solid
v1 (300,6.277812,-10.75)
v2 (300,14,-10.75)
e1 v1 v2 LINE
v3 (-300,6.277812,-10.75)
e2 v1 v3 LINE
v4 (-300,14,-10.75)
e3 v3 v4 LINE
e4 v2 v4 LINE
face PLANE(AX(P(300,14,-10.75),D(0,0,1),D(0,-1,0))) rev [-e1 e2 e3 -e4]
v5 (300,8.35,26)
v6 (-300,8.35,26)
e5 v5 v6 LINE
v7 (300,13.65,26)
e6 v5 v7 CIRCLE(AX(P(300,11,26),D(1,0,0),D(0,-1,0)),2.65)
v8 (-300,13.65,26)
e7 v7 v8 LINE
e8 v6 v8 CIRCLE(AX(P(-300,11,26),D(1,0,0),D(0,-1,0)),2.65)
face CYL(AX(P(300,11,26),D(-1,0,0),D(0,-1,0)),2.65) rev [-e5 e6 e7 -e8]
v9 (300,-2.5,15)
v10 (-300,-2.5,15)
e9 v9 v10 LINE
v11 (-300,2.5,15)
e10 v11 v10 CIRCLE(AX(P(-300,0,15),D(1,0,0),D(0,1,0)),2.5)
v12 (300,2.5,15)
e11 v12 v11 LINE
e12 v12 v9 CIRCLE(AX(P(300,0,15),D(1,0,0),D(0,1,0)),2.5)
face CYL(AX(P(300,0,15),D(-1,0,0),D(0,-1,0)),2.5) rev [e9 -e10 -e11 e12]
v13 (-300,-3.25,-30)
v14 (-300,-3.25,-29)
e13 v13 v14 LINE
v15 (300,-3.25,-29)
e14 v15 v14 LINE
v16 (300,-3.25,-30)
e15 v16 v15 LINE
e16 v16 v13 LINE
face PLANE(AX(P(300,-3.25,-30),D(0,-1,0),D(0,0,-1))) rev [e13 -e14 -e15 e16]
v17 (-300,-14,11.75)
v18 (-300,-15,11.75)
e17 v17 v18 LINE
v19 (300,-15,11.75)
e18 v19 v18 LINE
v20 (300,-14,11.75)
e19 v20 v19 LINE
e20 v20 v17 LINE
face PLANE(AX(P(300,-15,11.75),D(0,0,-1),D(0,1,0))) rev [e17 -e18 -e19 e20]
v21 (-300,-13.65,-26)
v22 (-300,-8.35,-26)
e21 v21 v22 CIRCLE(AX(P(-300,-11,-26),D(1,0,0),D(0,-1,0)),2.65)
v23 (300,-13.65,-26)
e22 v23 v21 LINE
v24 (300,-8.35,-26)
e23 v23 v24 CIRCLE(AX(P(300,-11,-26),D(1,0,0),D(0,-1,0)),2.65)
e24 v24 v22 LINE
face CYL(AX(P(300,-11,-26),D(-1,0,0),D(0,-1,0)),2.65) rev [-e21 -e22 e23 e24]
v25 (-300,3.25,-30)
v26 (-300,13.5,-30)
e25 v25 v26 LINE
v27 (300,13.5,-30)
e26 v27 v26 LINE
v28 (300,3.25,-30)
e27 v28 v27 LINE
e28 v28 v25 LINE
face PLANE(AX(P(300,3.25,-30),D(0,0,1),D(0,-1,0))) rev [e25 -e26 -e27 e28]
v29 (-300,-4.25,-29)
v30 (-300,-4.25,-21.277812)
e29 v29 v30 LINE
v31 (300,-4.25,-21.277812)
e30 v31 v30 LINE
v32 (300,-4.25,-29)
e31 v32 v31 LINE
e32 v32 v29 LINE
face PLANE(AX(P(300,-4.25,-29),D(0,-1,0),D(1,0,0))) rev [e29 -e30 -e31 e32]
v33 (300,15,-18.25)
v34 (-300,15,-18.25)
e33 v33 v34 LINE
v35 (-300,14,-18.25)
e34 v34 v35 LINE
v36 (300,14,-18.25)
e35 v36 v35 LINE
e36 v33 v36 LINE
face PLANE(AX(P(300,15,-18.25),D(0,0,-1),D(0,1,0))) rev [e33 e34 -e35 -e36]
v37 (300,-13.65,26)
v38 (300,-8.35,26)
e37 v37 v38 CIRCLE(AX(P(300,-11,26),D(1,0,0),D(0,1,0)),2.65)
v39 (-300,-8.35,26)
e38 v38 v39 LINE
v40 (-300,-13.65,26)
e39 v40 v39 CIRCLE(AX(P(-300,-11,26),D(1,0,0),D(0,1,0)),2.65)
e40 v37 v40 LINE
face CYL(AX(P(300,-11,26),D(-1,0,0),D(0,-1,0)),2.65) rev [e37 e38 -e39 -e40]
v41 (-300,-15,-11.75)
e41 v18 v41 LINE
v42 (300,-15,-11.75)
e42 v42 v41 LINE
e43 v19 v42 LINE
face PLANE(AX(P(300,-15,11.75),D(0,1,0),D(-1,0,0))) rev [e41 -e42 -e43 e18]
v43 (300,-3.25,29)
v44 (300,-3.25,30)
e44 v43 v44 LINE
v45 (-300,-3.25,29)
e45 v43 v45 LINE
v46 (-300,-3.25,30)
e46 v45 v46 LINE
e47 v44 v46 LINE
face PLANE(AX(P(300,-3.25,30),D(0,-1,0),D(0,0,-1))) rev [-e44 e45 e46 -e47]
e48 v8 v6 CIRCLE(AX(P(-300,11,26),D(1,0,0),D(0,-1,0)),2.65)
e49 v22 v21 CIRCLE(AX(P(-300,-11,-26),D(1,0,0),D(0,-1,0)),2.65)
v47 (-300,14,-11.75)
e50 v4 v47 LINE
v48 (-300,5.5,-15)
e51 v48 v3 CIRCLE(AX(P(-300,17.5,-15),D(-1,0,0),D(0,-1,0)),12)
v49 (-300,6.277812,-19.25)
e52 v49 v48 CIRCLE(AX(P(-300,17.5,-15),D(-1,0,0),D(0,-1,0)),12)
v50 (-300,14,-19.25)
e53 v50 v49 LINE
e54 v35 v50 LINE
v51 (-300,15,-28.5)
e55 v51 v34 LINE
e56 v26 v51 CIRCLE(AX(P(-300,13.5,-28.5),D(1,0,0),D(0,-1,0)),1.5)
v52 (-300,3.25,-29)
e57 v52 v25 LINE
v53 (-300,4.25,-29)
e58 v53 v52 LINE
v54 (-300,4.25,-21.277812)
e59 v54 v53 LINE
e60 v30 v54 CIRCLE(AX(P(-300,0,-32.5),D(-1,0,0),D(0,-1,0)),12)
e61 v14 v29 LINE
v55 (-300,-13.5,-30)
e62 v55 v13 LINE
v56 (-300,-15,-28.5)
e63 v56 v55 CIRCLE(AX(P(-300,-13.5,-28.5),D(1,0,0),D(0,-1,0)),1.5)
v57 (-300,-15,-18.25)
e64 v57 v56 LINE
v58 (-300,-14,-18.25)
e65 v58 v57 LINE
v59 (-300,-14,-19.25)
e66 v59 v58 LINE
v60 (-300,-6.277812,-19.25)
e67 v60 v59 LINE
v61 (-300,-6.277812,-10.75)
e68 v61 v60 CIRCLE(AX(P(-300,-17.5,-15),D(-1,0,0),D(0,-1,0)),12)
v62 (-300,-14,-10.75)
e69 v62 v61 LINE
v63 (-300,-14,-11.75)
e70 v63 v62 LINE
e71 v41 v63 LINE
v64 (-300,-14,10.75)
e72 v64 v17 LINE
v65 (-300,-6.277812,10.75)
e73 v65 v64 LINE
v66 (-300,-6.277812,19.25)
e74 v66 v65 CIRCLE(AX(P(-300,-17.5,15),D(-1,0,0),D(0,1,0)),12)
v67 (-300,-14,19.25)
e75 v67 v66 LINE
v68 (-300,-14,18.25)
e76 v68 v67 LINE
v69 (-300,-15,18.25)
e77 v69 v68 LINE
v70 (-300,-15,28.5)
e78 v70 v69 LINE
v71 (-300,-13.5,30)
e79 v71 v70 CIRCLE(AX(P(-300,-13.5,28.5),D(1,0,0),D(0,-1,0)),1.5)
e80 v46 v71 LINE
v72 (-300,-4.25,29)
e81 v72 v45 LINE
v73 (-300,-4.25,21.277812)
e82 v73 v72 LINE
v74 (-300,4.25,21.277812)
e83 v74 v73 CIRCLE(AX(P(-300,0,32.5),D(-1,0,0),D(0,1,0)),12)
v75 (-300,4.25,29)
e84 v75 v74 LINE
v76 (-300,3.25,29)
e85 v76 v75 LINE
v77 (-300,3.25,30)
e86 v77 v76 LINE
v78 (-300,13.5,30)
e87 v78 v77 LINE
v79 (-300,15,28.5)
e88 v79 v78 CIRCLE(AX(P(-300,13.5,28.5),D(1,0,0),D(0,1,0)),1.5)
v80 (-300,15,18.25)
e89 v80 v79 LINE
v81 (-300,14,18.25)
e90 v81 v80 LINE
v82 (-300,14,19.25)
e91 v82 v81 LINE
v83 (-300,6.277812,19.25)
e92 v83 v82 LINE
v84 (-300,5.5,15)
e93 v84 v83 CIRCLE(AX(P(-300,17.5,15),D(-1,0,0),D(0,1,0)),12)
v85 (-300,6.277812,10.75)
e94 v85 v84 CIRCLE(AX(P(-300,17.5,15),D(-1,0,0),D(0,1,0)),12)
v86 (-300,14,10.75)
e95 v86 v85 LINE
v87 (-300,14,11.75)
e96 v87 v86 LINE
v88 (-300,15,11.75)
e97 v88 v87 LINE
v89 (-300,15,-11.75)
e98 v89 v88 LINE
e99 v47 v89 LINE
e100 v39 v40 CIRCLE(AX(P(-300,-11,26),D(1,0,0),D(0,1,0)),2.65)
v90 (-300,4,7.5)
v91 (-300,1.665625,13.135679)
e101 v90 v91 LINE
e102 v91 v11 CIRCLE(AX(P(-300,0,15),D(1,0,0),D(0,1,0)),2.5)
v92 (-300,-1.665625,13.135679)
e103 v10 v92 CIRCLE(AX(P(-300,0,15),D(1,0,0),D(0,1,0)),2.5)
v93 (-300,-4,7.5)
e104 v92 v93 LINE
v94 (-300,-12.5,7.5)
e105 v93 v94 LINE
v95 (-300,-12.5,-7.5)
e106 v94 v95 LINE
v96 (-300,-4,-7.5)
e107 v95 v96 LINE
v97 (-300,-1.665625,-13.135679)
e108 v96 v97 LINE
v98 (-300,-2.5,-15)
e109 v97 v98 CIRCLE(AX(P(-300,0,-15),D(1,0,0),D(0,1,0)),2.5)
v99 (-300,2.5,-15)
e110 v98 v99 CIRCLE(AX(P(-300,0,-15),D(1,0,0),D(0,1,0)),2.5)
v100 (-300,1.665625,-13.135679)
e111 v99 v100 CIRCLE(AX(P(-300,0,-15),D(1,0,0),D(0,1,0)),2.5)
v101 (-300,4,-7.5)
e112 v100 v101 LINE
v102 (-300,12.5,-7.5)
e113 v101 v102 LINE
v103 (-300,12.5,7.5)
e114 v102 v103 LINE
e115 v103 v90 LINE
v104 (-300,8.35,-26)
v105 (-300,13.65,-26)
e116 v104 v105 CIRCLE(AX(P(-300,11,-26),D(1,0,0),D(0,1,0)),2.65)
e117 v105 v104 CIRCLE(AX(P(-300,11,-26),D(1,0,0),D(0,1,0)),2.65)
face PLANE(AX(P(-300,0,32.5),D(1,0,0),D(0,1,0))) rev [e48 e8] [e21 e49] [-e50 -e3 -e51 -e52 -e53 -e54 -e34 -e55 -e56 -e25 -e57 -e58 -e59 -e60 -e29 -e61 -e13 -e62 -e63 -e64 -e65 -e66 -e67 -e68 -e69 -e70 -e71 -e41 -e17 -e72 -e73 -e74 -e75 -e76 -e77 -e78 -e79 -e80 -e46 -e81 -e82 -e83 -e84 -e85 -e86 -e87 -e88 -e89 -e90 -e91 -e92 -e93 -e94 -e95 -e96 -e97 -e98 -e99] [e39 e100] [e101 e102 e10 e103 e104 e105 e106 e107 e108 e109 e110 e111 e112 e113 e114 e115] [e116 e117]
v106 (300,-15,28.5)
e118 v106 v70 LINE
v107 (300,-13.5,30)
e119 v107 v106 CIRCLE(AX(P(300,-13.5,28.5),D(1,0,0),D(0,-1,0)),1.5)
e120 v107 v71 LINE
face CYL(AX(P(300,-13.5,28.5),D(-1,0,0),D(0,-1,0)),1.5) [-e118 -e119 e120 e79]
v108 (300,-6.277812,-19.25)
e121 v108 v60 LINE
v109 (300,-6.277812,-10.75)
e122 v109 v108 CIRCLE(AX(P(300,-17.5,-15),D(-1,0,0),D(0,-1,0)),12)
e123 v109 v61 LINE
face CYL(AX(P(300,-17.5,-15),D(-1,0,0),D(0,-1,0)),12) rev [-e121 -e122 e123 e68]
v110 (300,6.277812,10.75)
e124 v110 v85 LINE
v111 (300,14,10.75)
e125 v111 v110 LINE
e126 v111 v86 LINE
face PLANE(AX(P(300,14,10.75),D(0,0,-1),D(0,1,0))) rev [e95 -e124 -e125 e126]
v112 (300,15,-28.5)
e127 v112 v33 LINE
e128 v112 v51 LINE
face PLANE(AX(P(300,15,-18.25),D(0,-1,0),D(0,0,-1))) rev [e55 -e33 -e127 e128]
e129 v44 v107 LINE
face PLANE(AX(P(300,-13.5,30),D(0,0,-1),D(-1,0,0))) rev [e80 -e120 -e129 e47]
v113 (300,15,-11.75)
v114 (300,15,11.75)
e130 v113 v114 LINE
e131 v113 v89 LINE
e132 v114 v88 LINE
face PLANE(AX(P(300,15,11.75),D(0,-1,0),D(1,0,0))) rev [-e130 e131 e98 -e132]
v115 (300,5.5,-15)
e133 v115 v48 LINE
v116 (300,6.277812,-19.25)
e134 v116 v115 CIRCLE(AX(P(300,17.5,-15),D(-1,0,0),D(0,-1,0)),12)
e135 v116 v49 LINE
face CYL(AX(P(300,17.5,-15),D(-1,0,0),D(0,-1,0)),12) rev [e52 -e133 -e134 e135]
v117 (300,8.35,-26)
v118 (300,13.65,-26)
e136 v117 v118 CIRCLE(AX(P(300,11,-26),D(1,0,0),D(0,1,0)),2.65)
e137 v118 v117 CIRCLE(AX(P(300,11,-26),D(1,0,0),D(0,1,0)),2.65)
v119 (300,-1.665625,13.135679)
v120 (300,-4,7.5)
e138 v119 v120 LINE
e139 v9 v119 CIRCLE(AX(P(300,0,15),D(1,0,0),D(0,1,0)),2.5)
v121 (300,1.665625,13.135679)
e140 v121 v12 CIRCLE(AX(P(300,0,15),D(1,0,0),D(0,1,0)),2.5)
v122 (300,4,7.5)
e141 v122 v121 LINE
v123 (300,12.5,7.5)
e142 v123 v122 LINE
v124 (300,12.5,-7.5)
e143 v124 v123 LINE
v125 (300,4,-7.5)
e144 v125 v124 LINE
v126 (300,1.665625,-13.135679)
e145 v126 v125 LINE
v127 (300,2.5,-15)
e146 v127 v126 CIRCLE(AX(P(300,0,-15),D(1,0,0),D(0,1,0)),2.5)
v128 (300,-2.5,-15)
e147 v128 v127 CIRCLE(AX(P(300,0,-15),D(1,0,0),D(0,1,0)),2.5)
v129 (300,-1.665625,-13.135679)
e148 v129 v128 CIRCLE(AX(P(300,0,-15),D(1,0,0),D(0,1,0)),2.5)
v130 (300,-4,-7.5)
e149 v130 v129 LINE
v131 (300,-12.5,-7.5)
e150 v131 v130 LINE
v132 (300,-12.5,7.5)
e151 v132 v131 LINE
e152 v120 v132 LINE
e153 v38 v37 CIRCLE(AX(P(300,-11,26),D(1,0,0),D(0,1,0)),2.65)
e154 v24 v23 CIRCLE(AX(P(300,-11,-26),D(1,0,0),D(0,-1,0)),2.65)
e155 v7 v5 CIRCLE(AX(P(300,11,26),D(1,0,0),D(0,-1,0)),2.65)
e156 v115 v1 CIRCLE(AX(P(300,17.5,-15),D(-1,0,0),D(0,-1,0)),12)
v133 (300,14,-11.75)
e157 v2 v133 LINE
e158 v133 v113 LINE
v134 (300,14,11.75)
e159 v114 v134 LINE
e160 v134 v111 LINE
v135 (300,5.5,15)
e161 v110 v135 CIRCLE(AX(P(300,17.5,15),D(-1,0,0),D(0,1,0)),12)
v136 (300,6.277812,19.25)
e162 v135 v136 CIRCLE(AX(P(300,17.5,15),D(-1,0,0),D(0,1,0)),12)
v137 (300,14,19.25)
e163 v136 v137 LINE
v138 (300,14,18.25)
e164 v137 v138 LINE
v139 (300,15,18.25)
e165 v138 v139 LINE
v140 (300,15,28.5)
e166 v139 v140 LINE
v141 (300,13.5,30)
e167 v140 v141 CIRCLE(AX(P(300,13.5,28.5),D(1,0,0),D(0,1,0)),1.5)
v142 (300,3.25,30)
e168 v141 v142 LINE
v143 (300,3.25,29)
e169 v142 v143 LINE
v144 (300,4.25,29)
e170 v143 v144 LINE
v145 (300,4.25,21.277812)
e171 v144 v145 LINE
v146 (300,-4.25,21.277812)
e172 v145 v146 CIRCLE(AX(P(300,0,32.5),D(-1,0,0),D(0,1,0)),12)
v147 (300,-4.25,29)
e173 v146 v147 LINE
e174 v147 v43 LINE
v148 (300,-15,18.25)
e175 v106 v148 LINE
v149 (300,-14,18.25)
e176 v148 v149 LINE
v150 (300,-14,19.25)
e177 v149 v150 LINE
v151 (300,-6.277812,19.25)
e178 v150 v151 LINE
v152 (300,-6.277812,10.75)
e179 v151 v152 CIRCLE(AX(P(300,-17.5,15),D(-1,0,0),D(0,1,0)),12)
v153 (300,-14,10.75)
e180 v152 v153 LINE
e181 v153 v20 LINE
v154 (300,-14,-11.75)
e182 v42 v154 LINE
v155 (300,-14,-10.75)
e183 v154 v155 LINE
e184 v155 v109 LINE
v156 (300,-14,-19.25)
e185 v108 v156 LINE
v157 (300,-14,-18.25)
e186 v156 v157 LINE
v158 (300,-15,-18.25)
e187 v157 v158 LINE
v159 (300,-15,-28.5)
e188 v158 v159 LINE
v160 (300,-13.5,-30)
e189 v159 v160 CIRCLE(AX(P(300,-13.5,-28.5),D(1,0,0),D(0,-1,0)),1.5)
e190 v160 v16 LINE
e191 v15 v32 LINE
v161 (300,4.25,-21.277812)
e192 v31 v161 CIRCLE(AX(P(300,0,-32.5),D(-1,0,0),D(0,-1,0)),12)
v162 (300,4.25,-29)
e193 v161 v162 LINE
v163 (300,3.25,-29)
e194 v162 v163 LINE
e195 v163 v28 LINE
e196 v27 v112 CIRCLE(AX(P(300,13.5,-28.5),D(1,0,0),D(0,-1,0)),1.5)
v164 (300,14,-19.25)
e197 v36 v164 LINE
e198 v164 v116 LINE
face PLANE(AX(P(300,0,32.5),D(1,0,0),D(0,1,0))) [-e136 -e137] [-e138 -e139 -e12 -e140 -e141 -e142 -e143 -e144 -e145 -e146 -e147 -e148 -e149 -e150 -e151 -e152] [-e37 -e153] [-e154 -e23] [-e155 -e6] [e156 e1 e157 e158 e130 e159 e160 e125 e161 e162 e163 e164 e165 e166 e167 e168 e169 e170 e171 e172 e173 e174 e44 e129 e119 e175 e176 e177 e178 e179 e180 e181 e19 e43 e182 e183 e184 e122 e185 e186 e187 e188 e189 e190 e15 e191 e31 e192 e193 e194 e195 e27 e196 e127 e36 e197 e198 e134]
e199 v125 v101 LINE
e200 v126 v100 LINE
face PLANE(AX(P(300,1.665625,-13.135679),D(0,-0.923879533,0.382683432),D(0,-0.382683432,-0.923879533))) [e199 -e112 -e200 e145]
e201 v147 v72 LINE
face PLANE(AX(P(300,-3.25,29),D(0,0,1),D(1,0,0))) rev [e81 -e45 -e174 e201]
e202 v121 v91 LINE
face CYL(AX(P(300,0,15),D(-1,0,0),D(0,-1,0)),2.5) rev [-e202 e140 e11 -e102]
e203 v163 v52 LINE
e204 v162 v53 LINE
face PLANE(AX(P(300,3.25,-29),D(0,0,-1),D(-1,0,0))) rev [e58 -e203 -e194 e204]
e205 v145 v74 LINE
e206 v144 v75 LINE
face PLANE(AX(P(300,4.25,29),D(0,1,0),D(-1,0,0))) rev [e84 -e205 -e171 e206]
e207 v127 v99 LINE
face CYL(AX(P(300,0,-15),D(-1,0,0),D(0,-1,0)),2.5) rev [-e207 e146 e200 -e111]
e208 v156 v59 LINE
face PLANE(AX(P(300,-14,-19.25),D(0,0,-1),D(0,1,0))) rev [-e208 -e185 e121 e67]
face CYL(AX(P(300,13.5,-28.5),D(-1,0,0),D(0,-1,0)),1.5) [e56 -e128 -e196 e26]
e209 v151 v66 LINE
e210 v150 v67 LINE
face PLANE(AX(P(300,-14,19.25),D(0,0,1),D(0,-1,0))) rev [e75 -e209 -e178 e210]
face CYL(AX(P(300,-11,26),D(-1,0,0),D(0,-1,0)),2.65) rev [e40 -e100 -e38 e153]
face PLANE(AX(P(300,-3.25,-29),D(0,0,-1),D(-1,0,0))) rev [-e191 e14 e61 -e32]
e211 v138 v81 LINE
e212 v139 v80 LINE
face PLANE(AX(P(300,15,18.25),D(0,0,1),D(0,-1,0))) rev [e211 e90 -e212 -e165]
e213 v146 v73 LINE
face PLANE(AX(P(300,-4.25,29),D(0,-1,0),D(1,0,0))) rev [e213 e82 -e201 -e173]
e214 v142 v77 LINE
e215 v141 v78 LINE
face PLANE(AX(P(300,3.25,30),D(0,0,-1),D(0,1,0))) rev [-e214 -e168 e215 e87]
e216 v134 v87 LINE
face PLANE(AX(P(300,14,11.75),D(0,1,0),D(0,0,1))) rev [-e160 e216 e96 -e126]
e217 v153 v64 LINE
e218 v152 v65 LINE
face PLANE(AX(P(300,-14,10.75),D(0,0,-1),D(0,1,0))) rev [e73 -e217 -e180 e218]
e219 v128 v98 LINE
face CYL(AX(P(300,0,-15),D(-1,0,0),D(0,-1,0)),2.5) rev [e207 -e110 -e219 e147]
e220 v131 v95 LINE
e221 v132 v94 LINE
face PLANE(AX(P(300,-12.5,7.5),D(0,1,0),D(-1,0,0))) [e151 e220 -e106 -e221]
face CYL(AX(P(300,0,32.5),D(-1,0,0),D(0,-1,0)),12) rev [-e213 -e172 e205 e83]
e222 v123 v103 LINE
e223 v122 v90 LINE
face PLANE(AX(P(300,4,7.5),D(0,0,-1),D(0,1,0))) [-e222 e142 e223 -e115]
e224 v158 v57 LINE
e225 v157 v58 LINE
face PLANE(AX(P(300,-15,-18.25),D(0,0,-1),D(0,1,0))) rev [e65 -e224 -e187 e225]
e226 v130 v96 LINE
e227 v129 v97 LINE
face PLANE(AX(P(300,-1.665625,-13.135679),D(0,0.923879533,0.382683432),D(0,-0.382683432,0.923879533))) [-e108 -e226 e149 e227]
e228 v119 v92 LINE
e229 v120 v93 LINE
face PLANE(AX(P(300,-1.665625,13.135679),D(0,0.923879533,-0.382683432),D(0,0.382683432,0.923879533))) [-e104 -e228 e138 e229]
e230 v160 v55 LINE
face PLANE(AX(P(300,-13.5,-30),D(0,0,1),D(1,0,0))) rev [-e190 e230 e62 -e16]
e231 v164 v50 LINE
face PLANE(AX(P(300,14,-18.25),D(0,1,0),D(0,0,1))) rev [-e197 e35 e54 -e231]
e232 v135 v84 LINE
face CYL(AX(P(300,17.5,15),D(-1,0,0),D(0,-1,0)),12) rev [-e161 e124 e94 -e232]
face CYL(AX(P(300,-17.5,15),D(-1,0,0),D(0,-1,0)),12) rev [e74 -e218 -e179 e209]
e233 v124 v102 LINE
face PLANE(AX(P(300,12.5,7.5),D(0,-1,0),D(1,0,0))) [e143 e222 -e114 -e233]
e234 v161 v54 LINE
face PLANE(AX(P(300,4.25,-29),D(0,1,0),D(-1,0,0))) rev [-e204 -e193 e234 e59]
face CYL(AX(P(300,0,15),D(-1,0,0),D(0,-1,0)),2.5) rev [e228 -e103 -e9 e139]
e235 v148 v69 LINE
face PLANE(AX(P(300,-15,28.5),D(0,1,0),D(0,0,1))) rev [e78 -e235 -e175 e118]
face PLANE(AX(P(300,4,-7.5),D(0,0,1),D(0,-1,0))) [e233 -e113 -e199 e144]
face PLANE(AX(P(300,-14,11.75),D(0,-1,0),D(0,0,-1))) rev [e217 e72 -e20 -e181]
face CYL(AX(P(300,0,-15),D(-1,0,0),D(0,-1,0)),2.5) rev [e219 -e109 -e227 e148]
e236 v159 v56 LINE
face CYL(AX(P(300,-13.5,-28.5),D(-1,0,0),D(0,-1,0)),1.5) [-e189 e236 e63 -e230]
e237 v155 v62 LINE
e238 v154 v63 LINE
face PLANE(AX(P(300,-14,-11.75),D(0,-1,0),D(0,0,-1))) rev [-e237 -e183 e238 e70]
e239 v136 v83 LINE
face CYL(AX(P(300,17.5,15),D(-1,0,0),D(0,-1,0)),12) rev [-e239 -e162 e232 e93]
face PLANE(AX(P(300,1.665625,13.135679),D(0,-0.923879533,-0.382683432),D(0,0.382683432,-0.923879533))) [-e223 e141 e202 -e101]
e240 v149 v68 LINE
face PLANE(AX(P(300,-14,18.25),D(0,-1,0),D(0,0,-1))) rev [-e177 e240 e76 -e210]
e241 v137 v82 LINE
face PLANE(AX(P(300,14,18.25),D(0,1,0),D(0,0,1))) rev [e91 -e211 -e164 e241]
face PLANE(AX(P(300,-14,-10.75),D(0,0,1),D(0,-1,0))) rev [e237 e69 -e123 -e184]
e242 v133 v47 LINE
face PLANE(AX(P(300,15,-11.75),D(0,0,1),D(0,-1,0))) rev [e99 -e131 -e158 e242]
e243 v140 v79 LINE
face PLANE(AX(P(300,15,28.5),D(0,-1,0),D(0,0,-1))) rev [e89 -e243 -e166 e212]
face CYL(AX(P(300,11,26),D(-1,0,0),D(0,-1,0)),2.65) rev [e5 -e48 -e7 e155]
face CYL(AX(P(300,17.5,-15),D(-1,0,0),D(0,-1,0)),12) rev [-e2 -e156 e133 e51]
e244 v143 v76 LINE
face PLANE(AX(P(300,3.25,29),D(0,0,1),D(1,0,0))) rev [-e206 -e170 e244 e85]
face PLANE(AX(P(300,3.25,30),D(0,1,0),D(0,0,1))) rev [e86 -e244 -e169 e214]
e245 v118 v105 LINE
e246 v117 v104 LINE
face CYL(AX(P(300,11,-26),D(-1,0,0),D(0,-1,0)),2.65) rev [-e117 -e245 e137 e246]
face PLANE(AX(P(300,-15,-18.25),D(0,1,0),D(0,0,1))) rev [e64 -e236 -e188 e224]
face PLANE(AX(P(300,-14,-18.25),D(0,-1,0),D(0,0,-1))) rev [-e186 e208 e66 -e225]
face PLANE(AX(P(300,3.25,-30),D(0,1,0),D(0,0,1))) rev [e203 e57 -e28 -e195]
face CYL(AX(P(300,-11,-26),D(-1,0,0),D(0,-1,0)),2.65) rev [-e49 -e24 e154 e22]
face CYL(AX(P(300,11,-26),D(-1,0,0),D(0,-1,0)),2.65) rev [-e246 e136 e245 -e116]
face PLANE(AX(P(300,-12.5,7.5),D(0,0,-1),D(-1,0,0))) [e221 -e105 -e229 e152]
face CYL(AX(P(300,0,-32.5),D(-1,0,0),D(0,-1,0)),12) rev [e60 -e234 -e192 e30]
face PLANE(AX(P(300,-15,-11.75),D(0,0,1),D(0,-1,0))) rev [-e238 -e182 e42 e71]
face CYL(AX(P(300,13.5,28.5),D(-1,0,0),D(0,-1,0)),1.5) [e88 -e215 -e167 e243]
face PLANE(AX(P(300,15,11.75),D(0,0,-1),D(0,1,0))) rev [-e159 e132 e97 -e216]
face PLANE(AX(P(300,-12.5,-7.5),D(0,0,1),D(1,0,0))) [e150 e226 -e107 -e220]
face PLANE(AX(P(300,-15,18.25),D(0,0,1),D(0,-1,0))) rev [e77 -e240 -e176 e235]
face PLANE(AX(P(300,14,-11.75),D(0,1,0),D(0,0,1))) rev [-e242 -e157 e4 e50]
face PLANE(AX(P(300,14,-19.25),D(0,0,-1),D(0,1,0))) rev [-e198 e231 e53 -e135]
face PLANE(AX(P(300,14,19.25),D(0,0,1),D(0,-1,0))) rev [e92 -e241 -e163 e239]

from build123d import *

# Parameters (mm, degrees)
SKETCH1_R                 = 2.65
F_30_X_60G_X_R1_5_1_DEPTH = 600


with BuildPart() as part:
    # Sketch1 → 工业铝型材 30 X 60G X R1.5(1) (new body)
    with BuildSketch(Plane.YZ.offset(-300)):
        with BuildLine():
            Line((-3.25, 30), (-3.25, 29))
            Line((-3.25, 29), (-4.25, 29))
            Line((-4.25, 29), (-4.25, 21.277812156))
            ThreePointArc((-4.25, 21.277812156), (0, 20.5), (4.25, 21.277812156))
            Line((4.25, 21.277812156), (4.25, 29))
            Line((4.25, 29), (3.25, 29))
            Line((3.25, 29), (3.25, 30))
            Line((3.25, 30), (13.5, 30))
            ThreePointArc((13.5, 30), (14.560660172, 29.560660172), (15, 28.5))
            Line((15, 28.5), (15, 18.25))
            Line((15, 18.25), (14, 18.25))
            Line((14, 18.25), (14, 19.25))
            Line((14, 19.25), (6.277812156, 19.25))
            ThreePointArc((6.277812156, 19.25), (5.5, 15), (6.277812156, 10.75))
            Line((6.277812156, 10.75), (14, 10.75))
            Line((14, 10.75), (14, 11.75))
            Line((14, 11.75), (15, 11.75))
            Line((15, 11.75), (15, -11.75))
            Line((15, -11.75), (14, -11.75))
            Line((14, -11.75), (14, -10.75))
            Line((14, -10.75), (6.277812156, -10.75))
            ThreePointArc((6.277812156, -10.75), (5.5, -15), (6.277812156, -19.25))
            Line((6.277812156, -19.25), (14, -19.25))
            Line((14, -19.25), (14, -18.25))
            Line((14, -18.25), (15, -18.25))
            Line((15, -18.25), (15, -28.5))
            ThreePointArc((15, -28.5), (14.560660172, -29.560660172), (13.5, -30))
            Line((13.5, -30), (3.25, -30))
            Line((3.25, -30), (3.25, -29))
            Line((3.25, -29), (4.25, -29))
            Line((4.25, -29), (4.25, -21.277812156))
            ThreePointArc((4.25, -21.277812156), (0, -20.5), (-4.25, -21.277812156))
            Line((-4.25, -21.277812156), (-4.25, -29))
            Line((-4.25, -29), (-3.25, -29))
            Line((-3.25, -29), (-3.25, -30))
            Line((-3.25, -30), (-13.5, -30))
            ThreePointArc((-13.5, -30), (-14.560660172, -29.560660172), (-15, -28.5))
            Line((-15, -28.5), (-15, -18.25))
            Line((-15, -18.25), (-14, -18.25))
            Line((-14, -18.25), (-14, -19.25))
            Line((-14, -19.25), (-6.277812156, -19.25))
            ThreePointArc((-6.277812156, -19.25), (-5.5, -15), (-6.277812156, -10.75))
            Line((-6.277812156, -10.75), (-14, -10.75))
            Line((-14, -10.75), (-14, -11.75))
            Line((-14, -11.75), (-15, -11.75))
            Line((-15, -11.75), (-15, 11.75))
            Line((-15, 11.75), (-14, 11.75))
            Line((-14, 11.75), (-14, 10.75))
            Line((-14, 10.75), (-6.277812156, 10.75))
            ThreePointArc((-6.277812156, 10.75), (-5.5, 15), (-6.277812156, 19.25))
            Line((-6.277812156, 19.25), (-14, 19.25))
            Line((-14, 19.25), (-14, 18.25))
            Line((-14, 18.25), (-15, 18.25))
            Line((-15, 18.25), (-15, 28.5))
            ThreePointArc((-15, 28.5), (-14.560660172, 29.560660172), (-13.5, 30))
            Line((-13.5, 30), (-3.25, 30))
        make_face()
        with Locations((-11, 26)):
            Circle(SKETCH1_R, mode=Mode.SUBTRACT)
        with Locations((11, 26)):
            Circle(SKETCH1_R, mode=Mode.SUBTRACT)
        with Locations((11, -26)):
            Circle(SKETCH1_R, mode=Mode.SUBTRACT)
        with Locations((-11, -26)):
            Circle(SKETCH1_R, mode=Mode.SUBTRACT)
        with BuildLine():
            Line((-12.5, 7.5), (-4, 7.5))
            Line((-4, 7.5), (-1.665625283, 13.135679101))
            ThreePointArc((-1.665625283, 13.135679101), (0, 17.5), (1.665625283, 13.135679101))
            Line((1.665625283, 13.135679101), (4, 7.5))
            Line((4, 7.5), (12.5, 7.5))
            Line((12.5, 7.5), (12.5, -7.5))
            Line((12.5, -7.5), (4, -7.5))
            Line((4, -7.5), (1.665625283, -13.135679101))
            ThreePointArc((1.665625283, -13.135679101), (0, -17.5), (-1.665625283, -13.135679101))
            Line((-1.665625283, -13.135679101), (-4, -7.5))
            Line((-4, -7.5), (-12.5, -7.5))
            Line((-12.5, -7.5), (-12.5, 7.5))
        make_face(mode=Mode.SUBTRACT)
    extrude(amount=F_30_X_60G_X_R1_5_1_DEPTH)


solid = part.part
